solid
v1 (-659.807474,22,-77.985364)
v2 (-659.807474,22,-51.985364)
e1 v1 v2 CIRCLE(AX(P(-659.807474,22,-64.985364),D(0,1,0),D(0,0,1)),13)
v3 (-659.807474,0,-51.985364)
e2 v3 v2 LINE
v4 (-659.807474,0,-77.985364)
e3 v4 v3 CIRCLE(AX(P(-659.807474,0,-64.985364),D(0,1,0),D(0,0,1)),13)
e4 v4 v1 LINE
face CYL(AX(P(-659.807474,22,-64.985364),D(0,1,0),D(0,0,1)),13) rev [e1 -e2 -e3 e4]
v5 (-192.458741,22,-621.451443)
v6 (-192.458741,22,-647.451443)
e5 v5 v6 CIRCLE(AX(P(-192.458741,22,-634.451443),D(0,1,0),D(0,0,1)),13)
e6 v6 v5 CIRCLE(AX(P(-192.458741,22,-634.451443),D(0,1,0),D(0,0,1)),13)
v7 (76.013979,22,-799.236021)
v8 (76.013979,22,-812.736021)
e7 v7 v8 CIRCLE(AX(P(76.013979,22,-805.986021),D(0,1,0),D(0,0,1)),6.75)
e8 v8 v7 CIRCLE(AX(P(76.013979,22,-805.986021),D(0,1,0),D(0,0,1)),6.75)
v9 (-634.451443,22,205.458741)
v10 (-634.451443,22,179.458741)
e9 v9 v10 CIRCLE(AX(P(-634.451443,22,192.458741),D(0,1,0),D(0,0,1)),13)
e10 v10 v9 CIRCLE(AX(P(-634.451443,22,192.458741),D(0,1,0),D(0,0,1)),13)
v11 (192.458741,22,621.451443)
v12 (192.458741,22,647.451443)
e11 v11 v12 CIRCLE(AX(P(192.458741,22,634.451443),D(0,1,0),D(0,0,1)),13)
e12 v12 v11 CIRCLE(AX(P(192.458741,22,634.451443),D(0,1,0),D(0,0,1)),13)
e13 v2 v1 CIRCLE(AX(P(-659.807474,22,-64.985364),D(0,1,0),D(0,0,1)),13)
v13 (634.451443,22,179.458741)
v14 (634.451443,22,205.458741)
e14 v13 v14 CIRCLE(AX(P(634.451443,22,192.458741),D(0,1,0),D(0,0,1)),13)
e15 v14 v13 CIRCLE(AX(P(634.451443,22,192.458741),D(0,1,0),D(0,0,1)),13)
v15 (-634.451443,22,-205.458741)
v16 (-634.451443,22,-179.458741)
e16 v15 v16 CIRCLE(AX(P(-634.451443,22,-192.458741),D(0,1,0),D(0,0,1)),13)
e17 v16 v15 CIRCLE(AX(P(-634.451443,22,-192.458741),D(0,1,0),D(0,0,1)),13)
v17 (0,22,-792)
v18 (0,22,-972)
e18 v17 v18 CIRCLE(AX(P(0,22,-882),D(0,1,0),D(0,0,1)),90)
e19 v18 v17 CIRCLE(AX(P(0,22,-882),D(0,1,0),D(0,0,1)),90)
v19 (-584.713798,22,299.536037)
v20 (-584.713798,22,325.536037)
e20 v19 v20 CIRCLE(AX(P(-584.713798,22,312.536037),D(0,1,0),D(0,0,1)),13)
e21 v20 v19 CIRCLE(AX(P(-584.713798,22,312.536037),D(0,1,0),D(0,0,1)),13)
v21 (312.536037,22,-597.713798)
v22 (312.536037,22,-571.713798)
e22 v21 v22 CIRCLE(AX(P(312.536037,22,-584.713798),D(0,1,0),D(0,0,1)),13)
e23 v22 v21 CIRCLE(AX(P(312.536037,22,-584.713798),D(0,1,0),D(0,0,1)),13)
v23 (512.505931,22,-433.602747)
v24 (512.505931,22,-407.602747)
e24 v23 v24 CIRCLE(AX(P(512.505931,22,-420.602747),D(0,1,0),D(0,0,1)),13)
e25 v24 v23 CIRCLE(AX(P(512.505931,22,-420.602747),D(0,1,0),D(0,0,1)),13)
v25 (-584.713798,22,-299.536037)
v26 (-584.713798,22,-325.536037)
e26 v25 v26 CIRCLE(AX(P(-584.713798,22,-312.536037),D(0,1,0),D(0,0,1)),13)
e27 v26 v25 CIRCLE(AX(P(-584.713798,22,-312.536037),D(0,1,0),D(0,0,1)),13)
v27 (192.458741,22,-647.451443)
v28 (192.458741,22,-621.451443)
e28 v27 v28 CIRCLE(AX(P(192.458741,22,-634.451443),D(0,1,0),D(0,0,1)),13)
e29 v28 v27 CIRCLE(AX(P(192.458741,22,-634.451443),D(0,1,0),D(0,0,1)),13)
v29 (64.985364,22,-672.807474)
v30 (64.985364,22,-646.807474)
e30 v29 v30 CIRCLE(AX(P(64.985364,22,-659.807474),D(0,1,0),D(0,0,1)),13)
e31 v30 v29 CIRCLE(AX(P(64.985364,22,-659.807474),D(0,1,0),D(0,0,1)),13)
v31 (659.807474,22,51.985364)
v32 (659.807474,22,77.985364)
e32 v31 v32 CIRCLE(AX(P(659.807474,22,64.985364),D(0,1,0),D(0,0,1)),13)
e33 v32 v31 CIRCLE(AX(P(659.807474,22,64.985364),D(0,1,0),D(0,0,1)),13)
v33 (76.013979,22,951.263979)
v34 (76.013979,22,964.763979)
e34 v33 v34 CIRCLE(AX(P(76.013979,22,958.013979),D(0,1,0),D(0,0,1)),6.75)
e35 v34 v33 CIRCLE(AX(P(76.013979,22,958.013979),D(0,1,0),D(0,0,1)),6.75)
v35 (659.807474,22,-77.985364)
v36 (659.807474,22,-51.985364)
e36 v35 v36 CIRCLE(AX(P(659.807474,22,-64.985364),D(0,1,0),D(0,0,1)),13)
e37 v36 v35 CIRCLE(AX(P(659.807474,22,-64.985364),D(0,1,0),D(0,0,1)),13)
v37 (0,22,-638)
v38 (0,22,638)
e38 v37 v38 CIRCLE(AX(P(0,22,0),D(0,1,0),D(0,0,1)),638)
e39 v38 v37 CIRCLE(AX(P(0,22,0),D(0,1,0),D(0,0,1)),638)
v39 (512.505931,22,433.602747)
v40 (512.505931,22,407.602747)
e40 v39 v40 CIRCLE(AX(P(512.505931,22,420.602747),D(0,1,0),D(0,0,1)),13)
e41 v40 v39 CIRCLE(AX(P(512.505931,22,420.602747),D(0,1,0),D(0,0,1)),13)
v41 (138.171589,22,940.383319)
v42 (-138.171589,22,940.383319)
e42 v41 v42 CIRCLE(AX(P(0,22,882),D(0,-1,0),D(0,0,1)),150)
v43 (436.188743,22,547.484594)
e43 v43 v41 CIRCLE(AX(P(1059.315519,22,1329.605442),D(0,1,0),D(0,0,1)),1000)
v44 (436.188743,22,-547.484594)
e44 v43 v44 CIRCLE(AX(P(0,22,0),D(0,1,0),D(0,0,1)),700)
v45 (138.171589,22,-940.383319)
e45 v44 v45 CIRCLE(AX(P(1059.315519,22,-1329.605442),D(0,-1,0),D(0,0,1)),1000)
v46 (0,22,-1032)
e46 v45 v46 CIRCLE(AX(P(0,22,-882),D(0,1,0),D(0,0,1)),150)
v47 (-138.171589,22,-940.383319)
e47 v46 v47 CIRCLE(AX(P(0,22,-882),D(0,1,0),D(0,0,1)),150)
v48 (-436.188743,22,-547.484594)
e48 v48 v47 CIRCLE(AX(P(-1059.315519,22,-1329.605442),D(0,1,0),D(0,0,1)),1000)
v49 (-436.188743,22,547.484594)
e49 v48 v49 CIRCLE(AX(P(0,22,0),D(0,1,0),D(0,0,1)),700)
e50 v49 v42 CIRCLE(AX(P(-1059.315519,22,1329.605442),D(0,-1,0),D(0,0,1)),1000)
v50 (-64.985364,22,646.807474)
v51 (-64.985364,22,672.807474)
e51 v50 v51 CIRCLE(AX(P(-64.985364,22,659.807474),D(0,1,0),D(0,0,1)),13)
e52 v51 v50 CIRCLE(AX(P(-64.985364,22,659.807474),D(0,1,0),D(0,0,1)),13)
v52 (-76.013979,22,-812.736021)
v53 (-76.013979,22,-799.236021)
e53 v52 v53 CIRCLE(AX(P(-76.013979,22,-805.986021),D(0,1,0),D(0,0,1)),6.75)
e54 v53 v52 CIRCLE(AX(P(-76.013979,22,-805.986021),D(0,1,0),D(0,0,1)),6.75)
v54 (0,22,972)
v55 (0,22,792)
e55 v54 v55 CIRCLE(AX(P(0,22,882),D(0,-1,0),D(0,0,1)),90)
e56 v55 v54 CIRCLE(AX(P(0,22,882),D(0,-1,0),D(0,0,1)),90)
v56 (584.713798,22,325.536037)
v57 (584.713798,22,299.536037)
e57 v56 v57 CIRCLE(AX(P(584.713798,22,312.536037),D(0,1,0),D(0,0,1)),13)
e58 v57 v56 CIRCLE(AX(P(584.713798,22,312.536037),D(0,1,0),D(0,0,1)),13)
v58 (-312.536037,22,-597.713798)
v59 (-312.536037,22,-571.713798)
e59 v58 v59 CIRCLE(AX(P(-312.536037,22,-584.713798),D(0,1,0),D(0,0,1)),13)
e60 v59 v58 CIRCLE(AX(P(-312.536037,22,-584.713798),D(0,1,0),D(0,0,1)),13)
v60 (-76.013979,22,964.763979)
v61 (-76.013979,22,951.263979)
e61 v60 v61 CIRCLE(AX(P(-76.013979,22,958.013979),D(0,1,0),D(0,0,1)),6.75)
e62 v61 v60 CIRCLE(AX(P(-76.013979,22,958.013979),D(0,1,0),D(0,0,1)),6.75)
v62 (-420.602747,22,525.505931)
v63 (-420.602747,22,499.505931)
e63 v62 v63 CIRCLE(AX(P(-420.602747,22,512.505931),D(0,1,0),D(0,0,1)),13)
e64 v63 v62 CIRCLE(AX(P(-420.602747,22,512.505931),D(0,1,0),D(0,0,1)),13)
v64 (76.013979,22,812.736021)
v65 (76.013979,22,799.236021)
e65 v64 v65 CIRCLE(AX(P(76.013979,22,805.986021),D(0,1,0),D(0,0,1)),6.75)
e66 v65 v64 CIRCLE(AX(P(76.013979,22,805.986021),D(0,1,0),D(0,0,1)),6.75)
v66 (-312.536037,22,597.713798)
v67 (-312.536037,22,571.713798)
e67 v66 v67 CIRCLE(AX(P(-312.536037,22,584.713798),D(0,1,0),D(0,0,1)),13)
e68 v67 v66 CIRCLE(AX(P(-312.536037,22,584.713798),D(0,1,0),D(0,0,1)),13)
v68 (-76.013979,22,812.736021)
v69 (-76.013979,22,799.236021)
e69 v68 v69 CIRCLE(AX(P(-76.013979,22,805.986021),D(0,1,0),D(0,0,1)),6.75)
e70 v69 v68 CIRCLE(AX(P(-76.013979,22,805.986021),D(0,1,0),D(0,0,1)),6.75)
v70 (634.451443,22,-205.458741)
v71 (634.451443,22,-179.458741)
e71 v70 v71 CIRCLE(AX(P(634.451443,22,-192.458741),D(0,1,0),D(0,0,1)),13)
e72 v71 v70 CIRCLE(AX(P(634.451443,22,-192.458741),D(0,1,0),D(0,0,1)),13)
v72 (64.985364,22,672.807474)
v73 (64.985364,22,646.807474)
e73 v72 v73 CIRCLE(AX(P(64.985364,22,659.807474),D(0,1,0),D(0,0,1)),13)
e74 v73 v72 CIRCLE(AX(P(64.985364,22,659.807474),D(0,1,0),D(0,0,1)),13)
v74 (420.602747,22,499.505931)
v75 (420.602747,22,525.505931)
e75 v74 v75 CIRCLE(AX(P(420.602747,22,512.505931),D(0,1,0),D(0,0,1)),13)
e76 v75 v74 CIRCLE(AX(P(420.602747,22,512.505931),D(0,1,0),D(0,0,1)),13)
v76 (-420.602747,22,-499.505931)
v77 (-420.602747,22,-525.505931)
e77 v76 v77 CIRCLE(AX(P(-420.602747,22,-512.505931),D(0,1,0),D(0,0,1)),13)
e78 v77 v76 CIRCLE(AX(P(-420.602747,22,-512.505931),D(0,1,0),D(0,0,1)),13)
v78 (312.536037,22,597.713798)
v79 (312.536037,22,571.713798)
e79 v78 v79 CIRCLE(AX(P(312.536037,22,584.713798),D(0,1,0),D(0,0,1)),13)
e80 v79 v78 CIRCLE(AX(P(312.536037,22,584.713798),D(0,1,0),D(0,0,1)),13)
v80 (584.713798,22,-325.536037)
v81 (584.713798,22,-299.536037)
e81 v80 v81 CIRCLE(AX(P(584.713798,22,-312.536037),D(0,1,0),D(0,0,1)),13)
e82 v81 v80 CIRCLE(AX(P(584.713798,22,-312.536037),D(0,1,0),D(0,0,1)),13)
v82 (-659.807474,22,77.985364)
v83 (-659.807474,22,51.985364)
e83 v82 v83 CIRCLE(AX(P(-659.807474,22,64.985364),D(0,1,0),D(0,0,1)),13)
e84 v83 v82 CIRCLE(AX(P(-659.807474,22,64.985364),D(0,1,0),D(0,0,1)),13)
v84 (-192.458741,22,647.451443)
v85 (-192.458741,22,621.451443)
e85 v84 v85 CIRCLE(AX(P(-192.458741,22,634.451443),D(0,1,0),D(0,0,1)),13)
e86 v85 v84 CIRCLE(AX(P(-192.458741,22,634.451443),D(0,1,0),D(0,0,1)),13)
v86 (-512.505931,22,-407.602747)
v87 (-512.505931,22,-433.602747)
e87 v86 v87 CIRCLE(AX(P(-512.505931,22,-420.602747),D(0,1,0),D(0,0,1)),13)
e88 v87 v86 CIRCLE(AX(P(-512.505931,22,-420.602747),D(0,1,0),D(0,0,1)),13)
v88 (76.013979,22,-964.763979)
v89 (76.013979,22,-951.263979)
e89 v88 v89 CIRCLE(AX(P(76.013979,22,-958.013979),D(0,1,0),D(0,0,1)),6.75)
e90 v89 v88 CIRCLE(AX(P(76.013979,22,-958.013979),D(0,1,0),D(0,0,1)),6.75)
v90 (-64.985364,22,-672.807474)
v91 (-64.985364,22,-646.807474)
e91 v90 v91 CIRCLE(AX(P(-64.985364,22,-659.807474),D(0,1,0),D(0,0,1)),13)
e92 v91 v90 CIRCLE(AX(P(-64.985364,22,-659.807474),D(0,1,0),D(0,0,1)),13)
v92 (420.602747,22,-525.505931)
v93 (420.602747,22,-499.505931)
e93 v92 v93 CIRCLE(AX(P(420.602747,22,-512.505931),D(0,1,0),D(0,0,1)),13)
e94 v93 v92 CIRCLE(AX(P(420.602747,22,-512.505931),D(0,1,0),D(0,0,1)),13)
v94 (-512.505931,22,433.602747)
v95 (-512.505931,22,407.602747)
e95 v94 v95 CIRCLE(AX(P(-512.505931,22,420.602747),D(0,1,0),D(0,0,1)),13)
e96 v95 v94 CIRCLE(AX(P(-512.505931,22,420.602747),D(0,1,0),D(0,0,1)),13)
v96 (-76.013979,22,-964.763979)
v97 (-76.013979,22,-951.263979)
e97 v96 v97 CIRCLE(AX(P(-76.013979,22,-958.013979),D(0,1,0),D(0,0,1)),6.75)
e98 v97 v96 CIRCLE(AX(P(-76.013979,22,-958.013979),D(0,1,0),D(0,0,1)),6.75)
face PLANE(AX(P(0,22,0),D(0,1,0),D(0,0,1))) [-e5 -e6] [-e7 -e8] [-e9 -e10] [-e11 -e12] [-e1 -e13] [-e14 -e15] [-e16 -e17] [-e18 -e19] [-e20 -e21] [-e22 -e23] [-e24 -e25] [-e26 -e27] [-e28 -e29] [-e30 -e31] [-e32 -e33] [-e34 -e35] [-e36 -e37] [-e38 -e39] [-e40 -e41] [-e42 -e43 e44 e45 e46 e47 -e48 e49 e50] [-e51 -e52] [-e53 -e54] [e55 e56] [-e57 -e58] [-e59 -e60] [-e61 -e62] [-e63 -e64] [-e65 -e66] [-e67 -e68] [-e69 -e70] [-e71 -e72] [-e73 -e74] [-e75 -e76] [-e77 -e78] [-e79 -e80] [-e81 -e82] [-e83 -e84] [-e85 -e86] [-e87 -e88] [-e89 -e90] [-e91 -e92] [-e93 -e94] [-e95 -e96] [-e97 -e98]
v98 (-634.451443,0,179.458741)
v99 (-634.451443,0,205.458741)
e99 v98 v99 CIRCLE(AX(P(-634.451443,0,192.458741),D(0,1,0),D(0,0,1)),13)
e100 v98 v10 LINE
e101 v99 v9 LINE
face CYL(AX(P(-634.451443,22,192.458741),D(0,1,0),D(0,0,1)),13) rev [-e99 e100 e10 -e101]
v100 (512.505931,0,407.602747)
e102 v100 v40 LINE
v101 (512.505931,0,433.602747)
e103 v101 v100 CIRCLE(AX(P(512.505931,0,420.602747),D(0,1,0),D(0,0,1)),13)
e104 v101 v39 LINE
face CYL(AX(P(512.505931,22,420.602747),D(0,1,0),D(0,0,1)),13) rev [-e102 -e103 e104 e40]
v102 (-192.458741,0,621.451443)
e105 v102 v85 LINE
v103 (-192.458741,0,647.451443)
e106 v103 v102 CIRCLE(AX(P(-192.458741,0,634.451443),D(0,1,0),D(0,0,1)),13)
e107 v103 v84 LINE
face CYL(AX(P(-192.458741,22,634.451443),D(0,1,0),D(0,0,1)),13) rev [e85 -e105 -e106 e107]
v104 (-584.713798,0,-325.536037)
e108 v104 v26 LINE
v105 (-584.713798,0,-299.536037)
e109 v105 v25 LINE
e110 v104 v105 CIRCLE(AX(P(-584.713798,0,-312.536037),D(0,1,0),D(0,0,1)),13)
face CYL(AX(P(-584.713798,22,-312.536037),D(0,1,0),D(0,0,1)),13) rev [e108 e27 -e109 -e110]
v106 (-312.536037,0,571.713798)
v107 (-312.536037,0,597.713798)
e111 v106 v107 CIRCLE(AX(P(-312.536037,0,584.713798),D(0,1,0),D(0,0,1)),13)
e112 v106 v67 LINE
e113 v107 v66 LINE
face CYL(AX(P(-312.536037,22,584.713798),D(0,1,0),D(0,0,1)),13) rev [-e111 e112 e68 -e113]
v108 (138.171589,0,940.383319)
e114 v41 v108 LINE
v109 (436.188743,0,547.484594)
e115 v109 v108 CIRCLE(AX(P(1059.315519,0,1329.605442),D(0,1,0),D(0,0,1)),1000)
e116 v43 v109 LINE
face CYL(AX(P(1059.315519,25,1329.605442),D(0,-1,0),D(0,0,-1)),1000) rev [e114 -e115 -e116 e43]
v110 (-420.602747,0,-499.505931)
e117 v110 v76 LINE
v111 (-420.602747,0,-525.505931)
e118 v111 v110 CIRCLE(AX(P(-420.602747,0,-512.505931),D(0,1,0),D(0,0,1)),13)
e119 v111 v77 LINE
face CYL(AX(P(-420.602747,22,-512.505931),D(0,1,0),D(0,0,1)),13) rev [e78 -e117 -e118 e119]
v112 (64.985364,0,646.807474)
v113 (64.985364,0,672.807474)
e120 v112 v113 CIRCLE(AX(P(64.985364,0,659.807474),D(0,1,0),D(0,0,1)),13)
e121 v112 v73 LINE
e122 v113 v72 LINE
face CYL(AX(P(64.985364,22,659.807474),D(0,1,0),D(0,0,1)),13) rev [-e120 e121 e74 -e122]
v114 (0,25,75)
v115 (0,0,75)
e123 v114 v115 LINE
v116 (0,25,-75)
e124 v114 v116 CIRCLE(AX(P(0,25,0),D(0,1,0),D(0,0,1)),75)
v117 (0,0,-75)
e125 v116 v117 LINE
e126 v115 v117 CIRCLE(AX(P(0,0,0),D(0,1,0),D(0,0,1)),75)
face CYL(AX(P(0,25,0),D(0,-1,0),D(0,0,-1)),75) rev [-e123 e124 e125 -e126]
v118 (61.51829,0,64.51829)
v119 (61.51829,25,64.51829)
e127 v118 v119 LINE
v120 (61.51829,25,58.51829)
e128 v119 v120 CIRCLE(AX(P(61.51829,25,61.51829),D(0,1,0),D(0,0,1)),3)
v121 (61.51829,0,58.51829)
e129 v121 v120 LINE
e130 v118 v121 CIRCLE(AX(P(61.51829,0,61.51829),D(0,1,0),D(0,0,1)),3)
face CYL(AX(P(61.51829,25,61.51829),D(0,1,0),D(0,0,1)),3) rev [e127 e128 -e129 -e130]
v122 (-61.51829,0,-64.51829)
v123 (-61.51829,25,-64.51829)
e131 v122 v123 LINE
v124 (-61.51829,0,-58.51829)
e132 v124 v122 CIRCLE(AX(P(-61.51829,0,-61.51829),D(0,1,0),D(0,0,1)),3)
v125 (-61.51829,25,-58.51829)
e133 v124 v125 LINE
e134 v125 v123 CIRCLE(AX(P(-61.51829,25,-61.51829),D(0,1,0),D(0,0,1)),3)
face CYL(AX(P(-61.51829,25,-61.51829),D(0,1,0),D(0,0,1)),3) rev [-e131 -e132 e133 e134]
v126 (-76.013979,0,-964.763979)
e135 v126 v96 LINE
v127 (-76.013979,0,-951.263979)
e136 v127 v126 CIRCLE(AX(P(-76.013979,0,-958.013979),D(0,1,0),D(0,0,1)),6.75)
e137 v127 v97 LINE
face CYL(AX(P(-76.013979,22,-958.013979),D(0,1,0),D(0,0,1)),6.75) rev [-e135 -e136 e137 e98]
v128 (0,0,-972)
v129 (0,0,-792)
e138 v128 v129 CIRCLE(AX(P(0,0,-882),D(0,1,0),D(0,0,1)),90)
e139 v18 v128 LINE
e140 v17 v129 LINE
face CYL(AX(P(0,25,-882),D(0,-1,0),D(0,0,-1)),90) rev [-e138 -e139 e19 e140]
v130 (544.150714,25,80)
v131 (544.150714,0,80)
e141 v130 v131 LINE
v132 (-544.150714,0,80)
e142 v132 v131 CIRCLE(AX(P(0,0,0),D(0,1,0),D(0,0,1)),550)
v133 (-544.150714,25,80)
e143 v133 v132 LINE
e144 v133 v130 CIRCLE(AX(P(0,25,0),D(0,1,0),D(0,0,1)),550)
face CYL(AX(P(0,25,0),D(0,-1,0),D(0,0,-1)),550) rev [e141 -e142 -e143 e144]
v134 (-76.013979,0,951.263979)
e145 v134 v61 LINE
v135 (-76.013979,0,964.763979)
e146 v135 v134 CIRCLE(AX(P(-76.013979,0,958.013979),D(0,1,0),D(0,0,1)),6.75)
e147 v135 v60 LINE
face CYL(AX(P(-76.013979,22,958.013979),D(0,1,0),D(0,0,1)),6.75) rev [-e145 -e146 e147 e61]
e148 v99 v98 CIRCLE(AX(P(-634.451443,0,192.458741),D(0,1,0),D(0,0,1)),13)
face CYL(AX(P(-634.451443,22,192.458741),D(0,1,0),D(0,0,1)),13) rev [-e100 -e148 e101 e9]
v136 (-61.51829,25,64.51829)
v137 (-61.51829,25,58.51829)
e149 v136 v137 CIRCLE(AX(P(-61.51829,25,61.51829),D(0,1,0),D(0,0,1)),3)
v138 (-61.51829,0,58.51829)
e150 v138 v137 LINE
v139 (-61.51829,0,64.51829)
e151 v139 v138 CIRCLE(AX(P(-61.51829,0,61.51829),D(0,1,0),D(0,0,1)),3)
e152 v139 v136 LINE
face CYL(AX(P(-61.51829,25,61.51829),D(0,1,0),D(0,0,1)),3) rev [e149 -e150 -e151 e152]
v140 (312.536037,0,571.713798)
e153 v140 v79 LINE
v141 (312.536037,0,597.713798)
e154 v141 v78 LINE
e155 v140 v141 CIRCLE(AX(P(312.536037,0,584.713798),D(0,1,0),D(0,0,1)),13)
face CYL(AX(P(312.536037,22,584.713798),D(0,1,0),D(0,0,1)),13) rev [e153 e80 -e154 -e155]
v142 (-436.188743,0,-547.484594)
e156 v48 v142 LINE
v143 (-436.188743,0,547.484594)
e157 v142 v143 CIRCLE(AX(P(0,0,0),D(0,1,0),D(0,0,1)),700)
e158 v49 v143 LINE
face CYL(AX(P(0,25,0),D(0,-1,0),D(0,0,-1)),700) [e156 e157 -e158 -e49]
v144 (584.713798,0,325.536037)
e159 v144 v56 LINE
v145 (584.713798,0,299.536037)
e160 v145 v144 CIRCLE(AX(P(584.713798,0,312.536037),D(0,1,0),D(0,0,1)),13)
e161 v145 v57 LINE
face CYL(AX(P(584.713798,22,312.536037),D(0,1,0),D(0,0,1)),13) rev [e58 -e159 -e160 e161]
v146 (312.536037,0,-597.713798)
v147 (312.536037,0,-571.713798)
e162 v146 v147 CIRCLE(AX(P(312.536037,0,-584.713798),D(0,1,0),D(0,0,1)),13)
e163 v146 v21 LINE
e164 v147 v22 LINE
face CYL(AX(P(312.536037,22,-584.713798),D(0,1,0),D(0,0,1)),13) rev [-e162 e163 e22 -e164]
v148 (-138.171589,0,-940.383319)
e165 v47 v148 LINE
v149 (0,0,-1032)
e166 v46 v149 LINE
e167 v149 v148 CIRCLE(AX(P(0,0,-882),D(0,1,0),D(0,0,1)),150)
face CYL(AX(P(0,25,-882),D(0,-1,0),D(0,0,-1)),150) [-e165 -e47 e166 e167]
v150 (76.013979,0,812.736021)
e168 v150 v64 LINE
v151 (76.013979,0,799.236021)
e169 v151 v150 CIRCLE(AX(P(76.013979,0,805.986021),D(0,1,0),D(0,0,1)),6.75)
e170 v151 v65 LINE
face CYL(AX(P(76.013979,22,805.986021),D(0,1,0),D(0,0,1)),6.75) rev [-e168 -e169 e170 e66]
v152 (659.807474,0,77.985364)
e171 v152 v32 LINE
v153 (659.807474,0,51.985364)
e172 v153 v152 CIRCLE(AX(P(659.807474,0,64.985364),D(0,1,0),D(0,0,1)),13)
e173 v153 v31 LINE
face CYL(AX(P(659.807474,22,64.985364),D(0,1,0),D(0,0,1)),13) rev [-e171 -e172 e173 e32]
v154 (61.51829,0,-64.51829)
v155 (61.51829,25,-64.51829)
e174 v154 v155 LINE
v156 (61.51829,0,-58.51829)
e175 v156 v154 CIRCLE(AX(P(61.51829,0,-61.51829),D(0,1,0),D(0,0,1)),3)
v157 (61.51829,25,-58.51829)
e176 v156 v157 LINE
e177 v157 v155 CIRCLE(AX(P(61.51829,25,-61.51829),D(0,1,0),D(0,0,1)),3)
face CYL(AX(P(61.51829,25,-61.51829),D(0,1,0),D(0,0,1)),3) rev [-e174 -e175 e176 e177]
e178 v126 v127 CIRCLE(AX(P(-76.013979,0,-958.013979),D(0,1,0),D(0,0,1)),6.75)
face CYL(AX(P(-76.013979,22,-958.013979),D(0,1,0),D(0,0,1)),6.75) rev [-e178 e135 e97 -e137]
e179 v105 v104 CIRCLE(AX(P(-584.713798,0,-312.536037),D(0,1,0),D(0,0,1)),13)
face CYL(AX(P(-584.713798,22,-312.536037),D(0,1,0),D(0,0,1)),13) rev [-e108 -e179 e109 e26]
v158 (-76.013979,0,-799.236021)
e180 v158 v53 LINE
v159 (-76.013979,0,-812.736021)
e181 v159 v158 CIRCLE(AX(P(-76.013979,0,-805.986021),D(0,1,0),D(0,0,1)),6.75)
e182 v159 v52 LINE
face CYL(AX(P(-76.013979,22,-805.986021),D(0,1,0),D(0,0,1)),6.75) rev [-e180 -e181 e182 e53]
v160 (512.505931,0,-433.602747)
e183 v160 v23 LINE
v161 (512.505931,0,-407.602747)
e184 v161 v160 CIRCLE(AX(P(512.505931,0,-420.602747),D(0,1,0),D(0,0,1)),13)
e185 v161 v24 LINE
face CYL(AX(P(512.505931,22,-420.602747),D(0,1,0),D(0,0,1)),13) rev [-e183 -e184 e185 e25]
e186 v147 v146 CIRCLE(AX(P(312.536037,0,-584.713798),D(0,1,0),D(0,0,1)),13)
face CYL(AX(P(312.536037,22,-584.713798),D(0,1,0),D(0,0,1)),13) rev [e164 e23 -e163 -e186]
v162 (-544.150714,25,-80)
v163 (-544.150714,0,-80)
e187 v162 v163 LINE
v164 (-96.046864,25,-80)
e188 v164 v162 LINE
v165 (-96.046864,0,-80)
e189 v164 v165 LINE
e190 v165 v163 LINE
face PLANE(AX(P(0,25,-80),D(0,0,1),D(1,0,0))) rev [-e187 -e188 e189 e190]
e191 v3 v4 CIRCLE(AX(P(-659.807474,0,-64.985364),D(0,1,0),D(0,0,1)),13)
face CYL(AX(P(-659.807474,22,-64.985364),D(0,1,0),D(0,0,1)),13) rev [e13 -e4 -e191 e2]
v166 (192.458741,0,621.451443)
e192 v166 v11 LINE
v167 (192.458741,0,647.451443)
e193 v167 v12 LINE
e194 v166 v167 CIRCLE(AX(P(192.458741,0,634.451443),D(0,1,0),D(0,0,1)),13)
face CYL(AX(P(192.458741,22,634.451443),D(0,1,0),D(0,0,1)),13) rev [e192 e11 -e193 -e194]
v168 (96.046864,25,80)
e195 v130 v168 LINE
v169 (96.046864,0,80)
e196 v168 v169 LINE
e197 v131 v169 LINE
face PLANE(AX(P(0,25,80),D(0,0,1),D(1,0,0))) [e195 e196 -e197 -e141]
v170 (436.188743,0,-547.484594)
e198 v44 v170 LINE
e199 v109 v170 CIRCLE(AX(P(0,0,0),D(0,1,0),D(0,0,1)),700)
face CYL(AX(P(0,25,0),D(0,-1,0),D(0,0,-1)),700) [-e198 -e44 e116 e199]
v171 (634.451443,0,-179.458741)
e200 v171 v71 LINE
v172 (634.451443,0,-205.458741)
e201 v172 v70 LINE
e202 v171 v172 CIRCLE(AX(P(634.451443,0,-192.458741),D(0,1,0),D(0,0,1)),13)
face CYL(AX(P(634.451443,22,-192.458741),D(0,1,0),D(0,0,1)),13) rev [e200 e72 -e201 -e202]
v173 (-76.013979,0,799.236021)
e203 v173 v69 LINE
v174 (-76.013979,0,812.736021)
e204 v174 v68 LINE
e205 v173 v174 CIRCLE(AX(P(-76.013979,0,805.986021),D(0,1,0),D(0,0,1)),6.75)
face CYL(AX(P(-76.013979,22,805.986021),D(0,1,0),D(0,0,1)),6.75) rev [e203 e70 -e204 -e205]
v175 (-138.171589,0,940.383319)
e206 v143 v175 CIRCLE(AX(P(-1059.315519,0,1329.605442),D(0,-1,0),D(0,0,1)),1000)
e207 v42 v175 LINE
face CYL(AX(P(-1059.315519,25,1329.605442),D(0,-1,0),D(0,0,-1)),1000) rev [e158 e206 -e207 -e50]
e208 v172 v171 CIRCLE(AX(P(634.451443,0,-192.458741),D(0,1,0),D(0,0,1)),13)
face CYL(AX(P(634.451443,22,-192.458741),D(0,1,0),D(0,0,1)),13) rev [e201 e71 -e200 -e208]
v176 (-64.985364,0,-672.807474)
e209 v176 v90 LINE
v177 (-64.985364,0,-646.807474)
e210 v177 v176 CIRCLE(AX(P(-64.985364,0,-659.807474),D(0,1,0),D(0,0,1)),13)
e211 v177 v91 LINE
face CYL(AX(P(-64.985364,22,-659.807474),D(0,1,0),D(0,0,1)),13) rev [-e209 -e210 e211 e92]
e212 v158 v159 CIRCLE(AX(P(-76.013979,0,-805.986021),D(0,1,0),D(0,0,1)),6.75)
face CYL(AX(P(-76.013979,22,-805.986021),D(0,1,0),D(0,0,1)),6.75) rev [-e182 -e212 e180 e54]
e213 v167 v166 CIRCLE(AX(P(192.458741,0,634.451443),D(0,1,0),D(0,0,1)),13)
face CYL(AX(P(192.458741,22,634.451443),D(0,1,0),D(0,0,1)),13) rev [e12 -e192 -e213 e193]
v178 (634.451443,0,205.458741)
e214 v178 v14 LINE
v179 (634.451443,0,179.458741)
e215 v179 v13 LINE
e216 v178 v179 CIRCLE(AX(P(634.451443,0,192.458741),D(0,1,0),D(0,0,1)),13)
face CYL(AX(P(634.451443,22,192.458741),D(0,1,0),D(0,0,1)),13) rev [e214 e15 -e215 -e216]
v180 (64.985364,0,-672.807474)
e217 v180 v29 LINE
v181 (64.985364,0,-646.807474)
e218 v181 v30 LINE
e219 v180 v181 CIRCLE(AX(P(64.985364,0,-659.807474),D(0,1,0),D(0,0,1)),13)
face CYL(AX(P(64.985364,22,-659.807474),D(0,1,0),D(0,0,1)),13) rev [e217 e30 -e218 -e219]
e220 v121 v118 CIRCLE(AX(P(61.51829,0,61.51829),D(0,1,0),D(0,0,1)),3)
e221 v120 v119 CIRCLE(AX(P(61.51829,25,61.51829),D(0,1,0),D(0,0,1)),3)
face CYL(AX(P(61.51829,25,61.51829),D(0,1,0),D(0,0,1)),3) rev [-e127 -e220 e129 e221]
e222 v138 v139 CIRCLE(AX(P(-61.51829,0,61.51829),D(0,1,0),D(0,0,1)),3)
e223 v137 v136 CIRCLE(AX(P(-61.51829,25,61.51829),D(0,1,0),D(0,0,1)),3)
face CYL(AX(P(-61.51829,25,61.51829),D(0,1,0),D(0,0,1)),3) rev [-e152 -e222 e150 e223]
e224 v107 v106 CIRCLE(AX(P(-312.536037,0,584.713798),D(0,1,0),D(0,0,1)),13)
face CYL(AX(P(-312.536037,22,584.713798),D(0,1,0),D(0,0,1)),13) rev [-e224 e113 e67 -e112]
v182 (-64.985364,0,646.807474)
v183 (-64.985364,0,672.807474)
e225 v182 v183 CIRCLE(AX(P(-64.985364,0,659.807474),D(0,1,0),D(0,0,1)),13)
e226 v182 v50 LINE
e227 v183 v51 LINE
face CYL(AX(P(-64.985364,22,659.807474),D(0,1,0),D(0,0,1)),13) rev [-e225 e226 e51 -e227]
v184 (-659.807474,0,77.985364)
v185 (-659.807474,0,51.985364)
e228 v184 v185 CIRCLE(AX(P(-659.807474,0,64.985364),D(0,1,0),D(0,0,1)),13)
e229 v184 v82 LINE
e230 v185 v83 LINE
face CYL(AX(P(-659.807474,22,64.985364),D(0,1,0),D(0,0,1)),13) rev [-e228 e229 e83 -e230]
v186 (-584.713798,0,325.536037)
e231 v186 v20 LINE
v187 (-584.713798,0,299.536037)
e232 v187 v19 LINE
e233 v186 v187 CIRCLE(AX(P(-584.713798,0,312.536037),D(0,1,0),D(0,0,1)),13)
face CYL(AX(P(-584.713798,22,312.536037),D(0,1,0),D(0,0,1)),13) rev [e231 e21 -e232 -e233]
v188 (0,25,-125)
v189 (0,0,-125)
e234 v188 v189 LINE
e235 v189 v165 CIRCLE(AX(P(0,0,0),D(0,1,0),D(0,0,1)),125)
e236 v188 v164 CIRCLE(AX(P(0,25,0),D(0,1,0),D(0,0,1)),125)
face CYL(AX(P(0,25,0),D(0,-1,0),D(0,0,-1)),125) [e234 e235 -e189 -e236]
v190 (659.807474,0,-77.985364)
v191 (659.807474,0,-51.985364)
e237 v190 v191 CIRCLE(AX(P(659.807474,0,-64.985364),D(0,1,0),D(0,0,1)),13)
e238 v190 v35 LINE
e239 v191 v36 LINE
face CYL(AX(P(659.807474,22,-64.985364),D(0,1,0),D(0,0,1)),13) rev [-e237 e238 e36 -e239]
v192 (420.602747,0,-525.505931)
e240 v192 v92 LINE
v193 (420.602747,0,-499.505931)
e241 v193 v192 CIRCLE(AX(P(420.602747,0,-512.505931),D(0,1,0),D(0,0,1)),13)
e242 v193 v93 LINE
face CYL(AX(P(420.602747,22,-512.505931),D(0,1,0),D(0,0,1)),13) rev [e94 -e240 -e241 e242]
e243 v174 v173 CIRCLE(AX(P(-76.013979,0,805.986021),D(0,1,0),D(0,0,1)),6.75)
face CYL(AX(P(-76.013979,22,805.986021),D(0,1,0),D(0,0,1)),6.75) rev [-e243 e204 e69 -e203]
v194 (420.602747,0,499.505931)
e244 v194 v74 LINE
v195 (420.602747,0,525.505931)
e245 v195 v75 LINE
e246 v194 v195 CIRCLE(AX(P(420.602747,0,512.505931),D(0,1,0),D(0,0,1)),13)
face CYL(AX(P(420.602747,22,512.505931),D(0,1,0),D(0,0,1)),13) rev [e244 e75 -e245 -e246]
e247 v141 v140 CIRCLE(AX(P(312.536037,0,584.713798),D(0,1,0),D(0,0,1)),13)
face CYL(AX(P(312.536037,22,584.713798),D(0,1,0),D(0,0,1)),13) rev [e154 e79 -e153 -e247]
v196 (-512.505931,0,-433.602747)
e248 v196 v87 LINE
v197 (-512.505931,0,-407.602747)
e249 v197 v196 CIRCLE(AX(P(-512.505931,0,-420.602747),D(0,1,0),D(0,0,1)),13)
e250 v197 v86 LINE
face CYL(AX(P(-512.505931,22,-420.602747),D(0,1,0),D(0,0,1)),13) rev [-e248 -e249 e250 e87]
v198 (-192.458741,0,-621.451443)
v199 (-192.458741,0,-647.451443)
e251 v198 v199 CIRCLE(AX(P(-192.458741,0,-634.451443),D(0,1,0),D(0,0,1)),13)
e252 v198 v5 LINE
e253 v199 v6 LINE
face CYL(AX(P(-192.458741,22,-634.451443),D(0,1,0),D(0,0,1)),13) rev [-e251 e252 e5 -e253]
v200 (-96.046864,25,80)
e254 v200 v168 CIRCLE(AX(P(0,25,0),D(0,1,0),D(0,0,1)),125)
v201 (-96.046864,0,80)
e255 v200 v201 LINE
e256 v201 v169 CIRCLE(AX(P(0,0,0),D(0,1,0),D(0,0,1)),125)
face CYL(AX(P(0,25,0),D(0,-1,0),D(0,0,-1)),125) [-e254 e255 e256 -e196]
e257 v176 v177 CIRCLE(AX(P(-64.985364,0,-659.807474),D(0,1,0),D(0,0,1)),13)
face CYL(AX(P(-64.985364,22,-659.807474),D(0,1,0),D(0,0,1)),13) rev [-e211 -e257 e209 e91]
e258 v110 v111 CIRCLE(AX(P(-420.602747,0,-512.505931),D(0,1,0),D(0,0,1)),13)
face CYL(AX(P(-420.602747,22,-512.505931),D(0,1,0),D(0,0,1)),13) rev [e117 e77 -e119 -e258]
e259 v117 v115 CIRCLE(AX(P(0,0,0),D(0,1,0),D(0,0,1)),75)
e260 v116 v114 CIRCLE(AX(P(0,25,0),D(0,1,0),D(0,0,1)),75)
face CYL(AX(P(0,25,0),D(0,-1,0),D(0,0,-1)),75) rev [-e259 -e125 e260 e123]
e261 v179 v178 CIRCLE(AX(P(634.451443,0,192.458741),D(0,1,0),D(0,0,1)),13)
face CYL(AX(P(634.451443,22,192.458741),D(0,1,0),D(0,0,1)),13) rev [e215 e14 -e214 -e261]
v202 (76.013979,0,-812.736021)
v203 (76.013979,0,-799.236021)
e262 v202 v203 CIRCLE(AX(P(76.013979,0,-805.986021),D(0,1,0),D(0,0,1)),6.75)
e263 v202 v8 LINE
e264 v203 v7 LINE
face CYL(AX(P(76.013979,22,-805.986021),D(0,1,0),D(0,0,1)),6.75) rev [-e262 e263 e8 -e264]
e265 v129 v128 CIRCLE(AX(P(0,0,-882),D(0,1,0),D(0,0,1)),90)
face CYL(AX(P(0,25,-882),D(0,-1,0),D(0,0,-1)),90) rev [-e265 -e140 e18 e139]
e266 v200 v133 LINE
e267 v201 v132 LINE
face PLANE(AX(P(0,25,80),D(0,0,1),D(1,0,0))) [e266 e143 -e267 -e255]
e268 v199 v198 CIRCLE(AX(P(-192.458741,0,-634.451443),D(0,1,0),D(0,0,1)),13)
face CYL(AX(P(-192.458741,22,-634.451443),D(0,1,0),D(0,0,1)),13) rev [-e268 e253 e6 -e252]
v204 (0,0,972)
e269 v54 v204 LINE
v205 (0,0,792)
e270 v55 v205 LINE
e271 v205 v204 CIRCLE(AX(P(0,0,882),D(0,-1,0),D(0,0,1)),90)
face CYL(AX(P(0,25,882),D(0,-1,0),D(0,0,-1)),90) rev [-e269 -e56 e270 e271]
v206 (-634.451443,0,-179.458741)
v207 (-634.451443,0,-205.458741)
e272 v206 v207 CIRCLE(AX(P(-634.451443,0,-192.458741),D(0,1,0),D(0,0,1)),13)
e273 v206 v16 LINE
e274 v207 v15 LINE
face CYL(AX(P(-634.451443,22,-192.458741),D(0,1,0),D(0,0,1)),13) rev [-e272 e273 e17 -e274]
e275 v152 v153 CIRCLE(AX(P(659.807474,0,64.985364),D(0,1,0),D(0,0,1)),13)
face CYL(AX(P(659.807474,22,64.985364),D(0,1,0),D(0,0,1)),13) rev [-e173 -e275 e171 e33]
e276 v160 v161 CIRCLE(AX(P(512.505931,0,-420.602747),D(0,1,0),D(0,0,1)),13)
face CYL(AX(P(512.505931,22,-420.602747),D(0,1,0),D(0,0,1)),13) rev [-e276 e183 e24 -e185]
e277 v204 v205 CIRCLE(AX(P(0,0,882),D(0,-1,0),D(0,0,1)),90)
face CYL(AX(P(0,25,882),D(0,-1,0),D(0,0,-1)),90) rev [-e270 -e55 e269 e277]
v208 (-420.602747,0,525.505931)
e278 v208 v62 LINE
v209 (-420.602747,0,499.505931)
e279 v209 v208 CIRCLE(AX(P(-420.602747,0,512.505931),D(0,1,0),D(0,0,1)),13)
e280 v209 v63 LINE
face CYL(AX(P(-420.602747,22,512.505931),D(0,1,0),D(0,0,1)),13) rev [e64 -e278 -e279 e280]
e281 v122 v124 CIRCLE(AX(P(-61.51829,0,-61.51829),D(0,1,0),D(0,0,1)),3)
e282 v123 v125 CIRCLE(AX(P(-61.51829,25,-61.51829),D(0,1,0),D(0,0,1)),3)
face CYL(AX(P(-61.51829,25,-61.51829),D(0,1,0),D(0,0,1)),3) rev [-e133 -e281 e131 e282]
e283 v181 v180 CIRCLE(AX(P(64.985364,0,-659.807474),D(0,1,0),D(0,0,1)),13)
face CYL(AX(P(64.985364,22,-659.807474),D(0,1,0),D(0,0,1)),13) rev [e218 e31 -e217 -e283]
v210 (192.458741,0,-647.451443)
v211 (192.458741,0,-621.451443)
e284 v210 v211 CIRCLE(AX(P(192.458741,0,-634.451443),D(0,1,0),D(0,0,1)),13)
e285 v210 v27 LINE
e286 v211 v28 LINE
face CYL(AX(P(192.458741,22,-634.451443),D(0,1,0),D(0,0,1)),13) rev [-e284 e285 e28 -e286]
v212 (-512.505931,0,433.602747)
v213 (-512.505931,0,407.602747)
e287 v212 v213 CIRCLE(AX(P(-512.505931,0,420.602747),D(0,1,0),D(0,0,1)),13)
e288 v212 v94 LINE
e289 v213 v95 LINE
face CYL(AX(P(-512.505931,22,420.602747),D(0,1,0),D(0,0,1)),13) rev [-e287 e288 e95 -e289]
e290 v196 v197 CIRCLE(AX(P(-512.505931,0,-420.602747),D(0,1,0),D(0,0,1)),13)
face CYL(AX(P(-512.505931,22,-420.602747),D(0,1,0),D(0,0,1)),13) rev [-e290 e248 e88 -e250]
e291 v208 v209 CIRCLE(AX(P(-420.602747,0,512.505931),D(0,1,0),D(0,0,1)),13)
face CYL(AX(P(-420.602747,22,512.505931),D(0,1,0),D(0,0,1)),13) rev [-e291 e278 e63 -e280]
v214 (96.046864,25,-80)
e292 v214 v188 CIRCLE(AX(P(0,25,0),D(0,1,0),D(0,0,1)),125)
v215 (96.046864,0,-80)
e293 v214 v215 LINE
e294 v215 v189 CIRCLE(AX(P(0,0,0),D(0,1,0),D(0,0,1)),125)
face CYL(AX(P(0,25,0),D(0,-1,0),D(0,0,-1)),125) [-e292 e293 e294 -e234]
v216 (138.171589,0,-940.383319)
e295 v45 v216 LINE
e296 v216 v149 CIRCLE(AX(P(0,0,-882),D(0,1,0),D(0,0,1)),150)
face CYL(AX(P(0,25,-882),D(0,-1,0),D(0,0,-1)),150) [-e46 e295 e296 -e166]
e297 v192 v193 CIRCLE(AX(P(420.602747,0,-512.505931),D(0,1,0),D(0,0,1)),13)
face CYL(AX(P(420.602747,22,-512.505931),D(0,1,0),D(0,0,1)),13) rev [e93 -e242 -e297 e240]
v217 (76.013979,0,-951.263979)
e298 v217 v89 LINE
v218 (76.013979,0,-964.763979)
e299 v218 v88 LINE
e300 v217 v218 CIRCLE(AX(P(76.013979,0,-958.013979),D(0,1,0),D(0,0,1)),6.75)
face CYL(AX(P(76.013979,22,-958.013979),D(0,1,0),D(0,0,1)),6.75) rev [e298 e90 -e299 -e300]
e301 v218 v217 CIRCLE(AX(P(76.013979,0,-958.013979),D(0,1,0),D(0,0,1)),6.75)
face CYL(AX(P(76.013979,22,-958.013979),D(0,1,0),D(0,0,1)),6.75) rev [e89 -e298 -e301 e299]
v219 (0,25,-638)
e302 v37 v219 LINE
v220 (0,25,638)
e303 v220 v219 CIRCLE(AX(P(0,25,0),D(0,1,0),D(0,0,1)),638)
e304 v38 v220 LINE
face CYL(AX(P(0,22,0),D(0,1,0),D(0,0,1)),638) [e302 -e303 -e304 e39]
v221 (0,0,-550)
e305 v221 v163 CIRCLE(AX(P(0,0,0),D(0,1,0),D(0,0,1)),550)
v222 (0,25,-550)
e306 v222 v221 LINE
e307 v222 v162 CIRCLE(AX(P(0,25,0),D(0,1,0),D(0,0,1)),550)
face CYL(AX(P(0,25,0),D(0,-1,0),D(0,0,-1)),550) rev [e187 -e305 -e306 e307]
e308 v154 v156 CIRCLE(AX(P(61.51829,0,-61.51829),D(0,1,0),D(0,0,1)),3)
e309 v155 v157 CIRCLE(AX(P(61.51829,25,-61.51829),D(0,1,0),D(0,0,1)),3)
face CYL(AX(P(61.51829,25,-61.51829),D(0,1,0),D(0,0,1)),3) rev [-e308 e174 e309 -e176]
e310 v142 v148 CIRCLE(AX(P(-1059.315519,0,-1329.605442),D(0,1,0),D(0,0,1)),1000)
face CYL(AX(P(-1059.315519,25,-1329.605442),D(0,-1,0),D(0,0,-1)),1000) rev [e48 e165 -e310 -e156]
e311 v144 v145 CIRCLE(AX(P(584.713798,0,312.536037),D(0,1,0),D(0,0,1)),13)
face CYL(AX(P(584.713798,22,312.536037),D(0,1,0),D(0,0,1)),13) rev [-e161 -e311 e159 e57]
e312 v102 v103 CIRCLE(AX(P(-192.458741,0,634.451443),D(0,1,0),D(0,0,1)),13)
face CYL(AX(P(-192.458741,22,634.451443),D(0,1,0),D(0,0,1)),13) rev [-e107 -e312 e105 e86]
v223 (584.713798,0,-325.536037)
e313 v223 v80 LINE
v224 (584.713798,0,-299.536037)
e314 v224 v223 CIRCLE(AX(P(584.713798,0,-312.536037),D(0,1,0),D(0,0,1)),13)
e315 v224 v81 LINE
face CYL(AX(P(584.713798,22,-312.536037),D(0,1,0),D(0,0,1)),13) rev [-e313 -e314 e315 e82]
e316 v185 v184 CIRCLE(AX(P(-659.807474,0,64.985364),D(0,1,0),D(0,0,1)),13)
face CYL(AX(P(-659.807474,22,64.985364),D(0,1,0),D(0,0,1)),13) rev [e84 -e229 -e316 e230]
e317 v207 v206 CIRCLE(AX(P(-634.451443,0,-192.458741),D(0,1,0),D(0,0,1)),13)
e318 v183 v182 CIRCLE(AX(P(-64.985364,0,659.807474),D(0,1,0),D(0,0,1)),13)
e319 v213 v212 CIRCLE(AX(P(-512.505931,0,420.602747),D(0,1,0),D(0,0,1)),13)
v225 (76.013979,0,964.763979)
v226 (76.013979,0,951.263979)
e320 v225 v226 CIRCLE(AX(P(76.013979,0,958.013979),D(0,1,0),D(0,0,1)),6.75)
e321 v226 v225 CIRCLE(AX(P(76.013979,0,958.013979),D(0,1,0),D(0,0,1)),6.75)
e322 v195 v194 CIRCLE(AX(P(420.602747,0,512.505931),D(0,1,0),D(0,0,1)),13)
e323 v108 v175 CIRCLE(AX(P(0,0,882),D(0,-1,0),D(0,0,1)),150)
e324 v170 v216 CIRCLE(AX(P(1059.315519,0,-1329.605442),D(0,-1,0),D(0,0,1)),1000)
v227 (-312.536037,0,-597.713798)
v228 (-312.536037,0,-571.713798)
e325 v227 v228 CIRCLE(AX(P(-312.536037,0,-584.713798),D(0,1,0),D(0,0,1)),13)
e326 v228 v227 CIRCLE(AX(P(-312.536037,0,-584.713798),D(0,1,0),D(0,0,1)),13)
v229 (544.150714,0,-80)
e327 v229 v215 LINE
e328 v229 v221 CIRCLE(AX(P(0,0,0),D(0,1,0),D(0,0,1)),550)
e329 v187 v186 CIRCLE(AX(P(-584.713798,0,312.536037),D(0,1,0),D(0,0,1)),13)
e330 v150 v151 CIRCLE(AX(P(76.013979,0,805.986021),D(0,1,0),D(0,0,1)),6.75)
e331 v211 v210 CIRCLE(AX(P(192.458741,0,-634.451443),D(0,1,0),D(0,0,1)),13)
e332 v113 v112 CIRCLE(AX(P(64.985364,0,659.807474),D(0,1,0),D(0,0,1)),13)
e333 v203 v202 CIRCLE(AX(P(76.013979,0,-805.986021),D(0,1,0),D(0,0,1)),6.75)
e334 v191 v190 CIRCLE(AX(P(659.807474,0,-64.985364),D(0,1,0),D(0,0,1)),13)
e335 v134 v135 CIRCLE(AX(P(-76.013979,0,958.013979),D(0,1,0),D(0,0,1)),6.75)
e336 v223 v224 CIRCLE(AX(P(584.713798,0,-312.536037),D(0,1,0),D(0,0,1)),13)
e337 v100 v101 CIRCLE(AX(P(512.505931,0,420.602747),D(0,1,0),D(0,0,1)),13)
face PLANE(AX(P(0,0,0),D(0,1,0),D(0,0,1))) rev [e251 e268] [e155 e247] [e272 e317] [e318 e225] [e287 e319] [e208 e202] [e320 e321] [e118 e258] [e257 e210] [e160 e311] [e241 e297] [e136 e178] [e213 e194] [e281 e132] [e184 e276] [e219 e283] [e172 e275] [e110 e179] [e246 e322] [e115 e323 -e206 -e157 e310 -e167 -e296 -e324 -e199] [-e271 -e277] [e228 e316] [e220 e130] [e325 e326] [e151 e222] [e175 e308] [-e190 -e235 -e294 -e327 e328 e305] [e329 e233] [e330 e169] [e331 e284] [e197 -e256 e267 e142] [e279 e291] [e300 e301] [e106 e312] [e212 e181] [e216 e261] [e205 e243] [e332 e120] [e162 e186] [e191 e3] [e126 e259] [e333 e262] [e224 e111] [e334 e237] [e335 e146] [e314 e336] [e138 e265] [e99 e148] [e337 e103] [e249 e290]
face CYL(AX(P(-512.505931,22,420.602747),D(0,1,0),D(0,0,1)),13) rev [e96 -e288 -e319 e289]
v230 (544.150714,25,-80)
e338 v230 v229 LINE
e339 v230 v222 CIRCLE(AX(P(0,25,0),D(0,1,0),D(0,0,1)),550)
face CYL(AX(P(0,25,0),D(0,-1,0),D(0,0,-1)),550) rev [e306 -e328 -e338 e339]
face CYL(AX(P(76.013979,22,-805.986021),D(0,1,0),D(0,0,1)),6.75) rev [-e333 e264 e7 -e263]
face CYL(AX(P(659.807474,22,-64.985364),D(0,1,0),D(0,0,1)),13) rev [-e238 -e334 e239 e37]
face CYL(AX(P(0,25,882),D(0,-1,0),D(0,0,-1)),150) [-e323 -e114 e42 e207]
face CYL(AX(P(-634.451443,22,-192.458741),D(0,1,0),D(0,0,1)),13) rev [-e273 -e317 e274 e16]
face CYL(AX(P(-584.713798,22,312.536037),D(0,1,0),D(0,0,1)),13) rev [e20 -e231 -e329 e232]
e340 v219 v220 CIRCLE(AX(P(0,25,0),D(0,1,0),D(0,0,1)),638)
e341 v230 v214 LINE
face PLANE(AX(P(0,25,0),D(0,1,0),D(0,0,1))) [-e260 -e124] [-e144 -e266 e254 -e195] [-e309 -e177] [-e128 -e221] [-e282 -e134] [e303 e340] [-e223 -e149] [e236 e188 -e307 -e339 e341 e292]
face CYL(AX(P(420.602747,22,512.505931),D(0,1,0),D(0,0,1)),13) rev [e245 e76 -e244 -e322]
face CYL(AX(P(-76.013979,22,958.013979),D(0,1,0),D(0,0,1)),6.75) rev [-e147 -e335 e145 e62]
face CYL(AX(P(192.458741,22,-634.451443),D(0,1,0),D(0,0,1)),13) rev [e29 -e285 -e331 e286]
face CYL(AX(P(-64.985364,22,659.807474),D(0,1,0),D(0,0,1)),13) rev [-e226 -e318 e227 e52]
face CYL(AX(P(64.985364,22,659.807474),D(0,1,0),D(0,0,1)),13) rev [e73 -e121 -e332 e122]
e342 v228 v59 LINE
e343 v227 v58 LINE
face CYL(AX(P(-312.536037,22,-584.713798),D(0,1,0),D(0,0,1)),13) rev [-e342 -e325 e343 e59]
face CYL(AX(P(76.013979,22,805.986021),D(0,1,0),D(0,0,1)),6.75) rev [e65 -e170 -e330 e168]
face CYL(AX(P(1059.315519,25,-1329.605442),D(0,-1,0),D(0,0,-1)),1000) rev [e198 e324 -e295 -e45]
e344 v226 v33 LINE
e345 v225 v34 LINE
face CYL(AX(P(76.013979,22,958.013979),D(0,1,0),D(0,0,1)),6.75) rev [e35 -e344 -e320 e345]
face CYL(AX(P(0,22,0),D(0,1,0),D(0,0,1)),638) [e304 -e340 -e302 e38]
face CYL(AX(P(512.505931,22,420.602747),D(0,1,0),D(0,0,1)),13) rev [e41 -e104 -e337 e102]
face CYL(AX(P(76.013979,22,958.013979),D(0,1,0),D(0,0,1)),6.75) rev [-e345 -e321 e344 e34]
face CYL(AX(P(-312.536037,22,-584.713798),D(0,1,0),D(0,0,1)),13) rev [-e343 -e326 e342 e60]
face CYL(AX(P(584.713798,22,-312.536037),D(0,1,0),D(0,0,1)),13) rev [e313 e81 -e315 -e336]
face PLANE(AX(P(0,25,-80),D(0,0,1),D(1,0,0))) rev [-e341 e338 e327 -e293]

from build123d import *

# Parameters (mm, degrees)
SKETCH1_R                    = 75
SKETCH1_R_2                  = 90
BOSS_EXTRUDE1_DEPTH          = 25
SKETCH2_OUTSIDE_W            = 1900.828
SKETCH2_OUTSIDE_H            = 2564.828
SKETCH2_OUTSIDE_R            = 638
CUT_EXTRUDE1_DEPTH           = 3
F_24_5_24_5_DIAMETER_HOLE1_D = 26
F_6_0_6_DIAMETER_HOLE1_D     = 6
F_13_5_13_5_DIAMETER_HOLE1_D = 13.5


with BuildPart() as part:
    # Sketch1 → Boss-Extrude1 (new body)
    with BuildSketch(Plane(origin=(0, 0, 0), x_dir=(1, 0, 0), z_dir=(0, 1, 0))):
        with BuildLine():
            ThreePointArc((436.188742989, 547.484593838), (262.581338083, 725.275527763), (138.171589394, 940.383318545))
            ThreePointArc((138.171589394, 940.383318545), (0, 1032), (-138.171589394, 940.383318545))
            ThreePointArc((-138.171589394, 940.383318545), (-262.581338083, 725.275527763), (-436.188742989, 547.484593838))
            ThreePointArc((-436.188742989, 547.484593838), (-700, 0), (-436.188742989, -547.484593838))
            ThreePointArc((-436.188742989, -547.484593838), (-262.581338083, -725.275527763), (-138.171589394, -940.383318545))
            ThreePointArc((-138.171589394, -940.383318545), (0, -1032), (138.171589394, -940.383318545))
            ThreePointArc((138.171589394, -940.383318545), (262.581338083, -725.275527763), (436.188742989, -547.484593838))
            ThreePointArc((436.188742989, -547.484593838), (700, 0), (436.188742989, 547.484593838))
        make_face()
        with BuildLine():
            Line((544.150714417, 80), (96.046863561, 80))
            ThreePointArc((96.046863561, 80), (0, 125), (-96.046863561, 80))
            Line((-96.046863561, 80), (-544.150714417, 80))
            ThreePointArc((-544.150714417, 80), (0, 550), (544.150714417, 80))
        make_face(mode=Mode.SUBTRACT)
        with BuildLine():
            Line((-544.150714417, -80), (-96.046863561, -80))
            ThreePointArc((-96.046863561, -80), (0, -125), (96.046863561, -80))
            Line((96.046863561, -80), (544.150714417, -80))
            ThreePointArc((544.150714417, -80), (0, -550), (-544.150714417, -80))
        make_face(mode=Mode.SUBTRACT)
        with Locations(Location((0, 0, 0), (0, 0, 270))):
            Circle(SKETCH1_R, mode=Mode.SUBTRACT)
        with Locations(Location((0, 882, 0), (0, 0, 270))):
            Circle(SKETCH1_R_2, mode=Mode.SUBTRACT)
        with Locations(Location((0, -882, 0), (0, 0, 270))):
            Circle(SKETCH1_R_2, mode=Mode.SUBTRACT)
    extrude(amount=BOSS_EXTRUDE1_DEPTH)

    # Sketch2 outside → Cut-Extrude1 (cut)
    with BuildSketch(Plane(origin=(0, 25, 0), x_dir=(1, 0, 0), z_dir=(0, 1, 0))):
        Rectangle(SKETCH2_OUTSIDE_W, SKETCH2_OUTSIDE_H)
        with Locations(Location((0, 0, 0), (0, 0, 270))):
            Circle(SKETCH2_OUTSIDE_R, mode=Mode.SUBTRACT)
    extrude(amount=-CUT_EXTRUDE1_DEPTH, mode=Mode.SUBTRACT)

    # Ø24.5 (24.5) Diameter Hole1 (through all)
    with Locations(Plane(origin=(0, 22, 0), x_dir=(1, 0, 0), z_dir=(0, 1, 0))):
        with Locations((659.807473784, 64.985364038), (659.807473784, -64.985364038), (634.45144259, -192.45874102), (584.713798263, -312.536036516), (512.505930579, -420.6027474), (420.6027474, -512.505930579), (312.536036516, -584.713798263), (192.45874102, -634.45144259), (64.985364038, -659.807473784), (-64.985364038, -659.807473784), (-192.45874102, -634.45144259), (-312.536036516, -584.713798263), (-420.6027474, -512.505930579), (-512.505930579, -420.6027474), (-584.713798263, -312.536036516), (-634.45144259, -192.45874102), (-659.807473784, -64.985364038), (-659.807473784, 64.985364038), (-634.45144259, 192.45874102), (-584.713798263, 312.536036516), (-512.505930579, 420.6027474), (-420.6027474, 512.505930579), (-312.536036516, 584.713798263), (-192.45874102, 634.45144259), (-64.985364038, 659.807473784), (64.985364038, 659.807473784), (192.45874102, 634.45144259), (312.536036516, 584.713798263), (420.6027474, 512.505930579), (512.505930579, 420.6027474), (584.713798263, 312.536036516), (634.45144259, 192.45874102)):
            Hole(F_24_5_24_5_DIAMETER_HOLE1_D / 2)

    # Ø6.0 (6) Diameter Hole1 (through all)
    with Locations(Plane(origin=(0, 25, 0), x_dir=(1, 0, 0), z_dir=(0, 1, 0))):
        with Locations((-61.518289963, 61.518289963), (61.518289963, 61.518289963), (61.518289963, -61.518289963), (-61.518289963, -61.518289963)):
            Hole(F_6_0_6_DIAMETER_HOLE1_D / 2)

    # Ø13.5 (13.5) Diameter Hole1 (through all)
    with Locations(Plane(origin=(0, 22, 0), x_dir=(1, 0, 0), z_dir=(0, 1, 0))):
        with Locations((-76.013978978, 958.013978978), (76.013978978, 958.013978978), (76.013978978, 805.986021022), (-76.013978978, 805.986021022)):
            f_13_5_13_5_diameter_hole1 = Hole(F_13_5_13_5_DIAMETER_HOLE1_D / 2)

    # Mirror1: Ø13.5 (13.5) Diameter Hole1 across plane
    add(f_13_5_13_5_diameter_hole1.mirror(Plane.XY), mode=Mode.SUBTRACT)


solid = part.part
